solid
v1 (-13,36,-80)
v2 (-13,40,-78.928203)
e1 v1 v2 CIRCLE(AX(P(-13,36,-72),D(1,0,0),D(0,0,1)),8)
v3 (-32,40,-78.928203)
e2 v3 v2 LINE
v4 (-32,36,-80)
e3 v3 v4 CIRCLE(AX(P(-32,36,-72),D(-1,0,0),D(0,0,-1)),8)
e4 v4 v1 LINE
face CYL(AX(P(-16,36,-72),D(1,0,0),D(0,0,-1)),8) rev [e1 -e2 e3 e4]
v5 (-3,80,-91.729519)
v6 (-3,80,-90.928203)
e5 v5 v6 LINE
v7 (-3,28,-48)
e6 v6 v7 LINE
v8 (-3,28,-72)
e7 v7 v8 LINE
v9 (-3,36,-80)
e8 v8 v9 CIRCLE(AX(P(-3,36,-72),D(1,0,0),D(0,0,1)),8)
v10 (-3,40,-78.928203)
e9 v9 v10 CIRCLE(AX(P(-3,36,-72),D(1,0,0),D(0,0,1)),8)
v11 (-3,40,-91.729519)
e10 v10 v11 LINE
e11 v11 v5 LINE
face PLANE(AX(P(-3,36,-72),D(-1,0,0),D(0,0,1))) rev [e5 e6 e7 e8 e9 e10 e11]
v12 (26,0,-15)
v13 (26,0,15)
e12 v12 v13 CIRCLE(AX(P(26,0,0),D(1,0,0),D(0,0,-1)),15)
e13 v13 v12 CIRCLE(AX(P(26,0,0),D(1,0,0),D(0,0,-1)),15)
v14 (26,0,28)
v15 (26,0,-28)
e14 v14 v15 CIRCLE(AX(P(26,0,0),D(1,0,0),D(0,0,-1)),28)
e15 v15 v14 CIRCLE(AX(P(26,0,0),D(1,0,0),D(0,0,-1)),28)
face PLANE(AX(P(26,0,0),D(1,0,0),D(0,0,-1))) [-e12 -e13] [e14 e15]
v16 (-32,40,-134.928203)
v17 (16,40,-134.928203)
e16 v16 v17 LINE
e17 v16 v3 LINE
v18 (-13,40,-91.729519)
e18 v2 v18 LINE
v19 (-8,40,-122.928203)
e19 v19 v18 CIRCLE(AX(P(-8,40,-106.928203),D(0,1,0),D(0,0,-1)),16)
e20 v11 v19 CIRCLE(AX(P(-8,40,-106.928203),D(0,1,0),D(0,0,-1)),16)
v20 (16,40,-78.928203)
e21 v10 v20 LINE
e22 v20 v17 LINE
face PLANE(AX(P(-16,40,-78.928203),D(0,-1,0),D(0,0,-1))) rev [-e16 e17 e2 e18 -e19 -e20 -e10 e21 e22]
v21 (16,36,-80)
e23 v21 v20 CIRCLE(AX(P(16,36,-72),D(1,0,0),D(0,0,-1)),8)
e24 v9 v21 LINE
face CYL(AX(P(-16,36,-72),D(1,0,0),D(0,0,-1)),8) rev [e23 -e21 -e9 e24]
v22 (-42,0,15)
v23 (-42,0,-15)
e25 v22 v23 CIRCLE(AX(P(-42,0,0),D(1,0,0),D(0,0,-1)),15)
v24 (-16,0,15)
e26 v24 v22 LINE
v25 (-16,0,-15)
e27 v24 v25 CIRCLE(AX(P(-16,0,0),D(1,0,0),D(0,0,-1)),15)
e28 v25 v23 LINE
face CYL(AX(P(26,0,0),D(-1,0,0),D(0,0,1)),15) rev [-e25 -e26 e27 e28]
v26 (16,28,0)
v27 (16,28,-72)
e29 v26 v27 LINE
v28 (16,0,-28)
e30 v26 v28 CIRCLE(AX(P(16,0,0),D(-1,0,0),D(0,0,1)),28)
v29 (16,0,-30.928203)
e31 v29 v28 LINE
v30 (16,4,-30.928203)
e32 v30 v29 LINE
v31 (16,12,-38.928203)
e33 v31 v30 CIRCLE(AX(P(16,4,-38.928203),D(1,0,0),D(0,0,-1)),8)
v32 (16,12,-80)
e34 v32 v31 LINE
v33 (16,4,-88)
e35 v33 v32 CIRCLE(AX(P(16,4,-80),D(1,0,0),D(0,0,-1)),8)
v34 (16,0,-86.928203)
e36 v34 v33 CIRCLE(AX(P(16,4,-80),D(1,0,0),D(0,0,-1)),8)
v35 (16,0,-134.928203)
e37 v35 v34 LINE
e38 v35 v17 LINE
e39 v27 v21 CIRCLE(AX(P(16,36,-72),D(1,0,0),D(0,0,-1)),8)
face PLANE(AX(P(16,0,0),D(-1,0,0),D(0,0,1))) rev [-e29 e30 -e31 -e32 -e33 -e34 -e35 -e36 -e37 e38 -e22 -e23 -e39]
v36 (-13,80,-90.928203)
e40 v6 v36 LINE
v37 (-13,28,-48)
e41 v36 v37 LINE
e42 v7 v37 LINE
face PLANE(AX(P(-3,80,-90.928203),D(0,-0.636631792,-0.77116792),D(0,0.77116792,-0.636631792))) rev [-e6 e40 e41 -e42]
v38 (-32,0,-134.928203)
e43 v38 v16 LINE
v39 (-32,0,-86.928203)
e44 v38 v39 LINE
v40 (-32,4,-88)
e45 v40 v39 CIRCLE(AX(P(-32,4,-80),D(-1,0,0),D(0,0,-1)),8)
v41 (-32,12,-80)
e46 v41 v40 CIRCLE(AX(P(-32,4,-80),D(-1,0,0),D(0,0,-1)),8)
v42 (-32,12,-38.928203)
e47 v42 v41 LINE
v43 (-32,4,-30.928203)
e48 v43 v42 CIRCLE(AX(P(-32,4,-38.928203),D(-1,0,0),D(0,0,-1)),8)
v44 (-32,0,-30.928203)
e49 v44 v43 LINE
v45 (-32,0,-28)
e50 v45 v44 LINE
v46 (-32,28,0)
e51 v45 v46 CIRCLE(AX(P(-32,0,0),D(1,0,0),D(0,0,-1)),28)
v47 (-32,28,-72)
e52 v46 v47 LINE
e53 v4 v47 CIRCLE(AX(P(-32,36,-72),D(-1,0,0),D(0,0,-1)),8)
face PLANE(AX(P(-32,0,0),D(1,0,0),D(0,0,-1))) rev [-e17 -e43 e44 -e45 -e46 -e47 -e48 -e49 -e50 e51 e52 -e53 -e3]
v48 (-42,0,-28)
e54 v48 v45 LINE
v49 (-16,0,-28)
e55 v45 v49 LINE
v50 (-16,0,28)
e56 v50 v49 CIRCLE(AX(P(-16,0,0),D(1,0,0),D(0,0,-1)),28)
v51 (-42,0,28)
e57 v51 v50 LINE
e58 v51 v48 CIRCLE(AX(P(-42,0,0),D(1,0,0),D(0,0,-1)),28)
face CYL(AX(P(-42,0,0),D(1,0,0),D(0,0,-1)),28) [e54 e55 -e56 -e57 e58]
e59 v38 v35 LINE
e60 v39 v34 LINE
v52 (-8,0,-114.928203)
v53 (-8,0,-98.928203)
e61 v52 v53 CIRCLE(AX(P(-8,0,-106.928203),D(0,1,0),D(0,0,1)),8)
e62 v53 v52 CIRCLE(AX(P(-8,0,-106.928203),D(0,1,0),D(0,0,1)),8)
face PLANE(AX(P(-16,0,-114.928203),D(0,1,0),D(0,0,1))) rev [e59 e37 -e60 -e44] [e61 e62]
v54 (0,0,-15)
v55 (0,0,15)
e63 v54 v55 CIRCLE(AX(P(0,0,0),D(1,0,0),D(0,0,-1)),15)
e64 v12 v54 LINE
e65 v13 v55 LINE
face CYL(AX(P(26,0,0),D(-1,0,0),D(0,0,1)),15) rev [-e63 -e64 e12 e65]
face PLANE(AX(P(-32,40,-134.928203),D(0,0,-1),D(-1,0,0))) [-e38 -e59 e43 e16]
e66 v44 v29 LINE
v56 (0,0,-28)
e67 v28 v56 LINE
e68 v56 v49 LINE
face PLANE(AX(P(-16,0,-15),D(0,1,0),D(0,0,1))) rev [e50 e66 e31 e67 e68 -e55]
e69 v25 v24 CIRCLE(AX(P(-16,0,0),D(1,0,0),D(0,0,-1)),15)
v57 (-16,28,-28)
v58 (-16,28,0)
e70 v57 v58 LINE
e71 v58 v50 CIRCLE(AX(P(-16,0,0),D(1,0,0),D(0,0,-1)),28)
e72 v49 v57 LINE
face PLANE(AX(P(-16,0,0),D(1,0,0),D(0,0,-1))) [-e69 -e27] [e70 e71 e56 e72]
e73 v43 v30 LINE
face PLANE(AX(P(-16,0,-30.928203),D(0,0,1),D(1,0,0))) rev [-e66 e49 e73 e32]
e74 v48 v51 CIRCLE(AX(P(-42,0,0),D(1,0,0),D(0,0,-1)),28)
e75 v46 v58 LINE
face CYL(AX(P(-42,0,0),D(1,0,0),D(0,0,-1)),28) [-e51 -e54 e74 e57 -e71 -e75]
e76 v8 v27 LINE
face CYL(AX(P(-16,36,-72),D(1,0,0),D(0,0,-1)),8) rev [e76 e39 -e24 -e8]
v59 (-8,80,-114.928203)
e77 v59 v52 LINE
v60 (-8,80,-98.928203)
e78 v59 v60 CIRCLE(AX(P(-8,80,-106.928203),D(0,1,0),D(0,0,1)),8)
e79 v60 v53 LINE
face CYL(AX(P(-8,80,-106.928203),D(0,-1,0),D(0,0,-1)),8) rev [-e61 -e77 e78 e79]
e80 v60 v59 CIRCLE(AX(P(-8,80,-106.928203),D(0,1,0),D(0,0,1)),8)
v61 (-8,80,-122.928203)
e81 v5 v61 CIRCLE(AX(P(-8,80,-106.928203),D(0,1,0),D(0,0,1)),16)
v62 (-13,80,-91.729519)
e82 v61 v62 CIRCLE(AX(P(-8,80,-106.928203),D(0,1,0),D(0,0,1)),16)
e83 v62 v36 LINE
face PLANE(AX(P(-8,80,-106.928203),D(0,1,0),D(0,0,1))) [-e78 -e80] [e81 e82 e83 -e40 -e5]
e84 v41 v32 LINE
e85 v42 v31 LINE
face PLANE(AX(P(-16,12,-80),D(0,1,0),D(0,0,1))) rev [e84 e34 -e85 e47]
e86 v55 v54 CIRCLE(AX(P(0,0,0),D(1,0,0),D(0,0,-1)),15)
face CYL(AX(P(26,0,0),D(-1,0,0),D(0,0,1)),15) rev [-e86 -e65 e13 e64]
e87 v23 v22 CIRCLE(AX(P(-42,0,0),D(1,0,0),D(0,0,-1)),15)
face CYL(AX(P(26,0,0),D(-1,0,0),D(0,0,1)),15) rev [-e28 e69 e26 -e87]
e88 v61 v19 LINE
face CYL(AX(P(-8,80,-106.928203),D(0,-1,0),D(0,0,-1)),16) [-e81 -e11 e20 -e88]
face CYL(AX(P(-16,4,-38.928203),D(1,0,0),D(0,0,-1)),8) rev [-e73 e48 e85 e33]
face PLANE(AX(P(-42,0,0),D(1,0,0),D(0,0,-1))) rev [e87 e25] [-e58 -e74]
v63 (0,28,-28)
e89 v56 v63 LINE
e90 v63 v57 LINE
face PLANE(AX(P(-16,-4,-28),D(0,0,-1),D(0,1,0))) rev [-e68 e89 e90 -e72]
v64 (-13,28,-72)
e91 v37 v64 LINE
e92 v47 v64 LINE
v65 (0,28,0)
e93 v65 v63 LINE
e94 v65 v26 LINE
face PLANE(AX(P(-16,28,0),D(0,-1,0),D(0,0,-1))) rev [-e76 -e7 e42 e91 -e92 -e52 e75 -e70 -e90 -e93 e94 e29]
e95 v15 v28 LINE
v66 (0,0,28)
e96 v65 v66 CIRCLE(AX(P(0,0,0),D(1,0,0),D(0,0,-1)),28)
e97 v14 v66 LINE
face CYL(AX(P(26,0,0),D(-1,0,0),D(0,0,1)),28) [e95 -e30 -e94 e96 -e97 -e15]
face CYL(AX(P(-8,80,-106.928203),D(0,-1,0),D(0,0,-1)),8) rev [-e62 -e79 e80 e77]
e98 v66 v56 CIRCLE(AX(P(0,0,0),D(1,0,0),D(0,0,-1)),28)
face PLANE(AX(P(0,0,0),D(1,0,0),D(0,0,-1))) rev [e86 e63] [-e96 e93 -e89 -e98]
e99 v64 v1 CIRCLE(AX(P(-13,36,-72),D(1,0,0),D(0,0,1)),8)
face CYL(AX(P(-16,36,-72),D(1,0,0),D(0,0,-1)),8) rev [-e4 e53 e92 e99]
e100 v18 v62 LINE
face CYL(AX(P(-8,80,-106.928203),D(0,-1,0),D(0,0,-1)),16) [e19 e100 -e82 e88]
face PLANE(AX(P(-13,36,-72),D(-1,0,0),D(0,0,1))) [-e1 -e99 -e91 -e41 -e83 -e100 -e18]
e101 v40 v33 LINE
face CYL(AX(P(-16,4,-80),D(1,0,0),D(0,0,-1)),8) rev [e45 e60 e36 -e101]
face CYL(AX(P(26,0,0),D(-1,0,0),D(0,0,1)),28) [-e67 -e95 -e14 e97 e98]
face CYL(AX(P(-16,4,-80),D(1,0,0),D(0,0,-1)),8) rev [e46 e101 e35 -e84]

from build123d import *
from build123d.topology import SkipClean

# Parameters (mm, degrees)
CLEVIS_LUG_1_SKETCH_R     = 28
CLEVIS_LUG_1_SKETCH_R_2   = 15
CLEVIS_LUG_1_56X_30_DEPTH = 26
CLEVIS_LUG_2_SKETCH_R     = 28
CLEVIS_LUG_2_SKETCH_R_2   = 15
CLEVIS_LUG_2_56X_30_DEPTH = 26
ARM_START                 = -16
ARM_BODY_DEPTH            = 16
ARM_EXTENSION_DEPTH       = 16
FORK_SLOT_SKETCH_W        = 16
FORK_SLOT_SKETCH_H        = 28
FORK_SLOT_CUT_DEPTH       = 32
PIVOT_BLOCK_SKETCH_W      = 39.579982786
PIVOT_BLOCK_SKETCH_H      = 40
PIVOT_BLOCK_DEPTH         = 48
TOP_PIVOT_BOSS_SKETCH_R   = 16
TOP_PIVOT_BOSS_SKETCH_R_2 = 8
TOP_PIVOT_BOSS_32_DEPTH   = 40
PIVOT_START               = -40
PIVOT_BORE_SKETCH_R       = 8
PIVOT_BORE_16_DEPTH       = 40
BOSS_GUSSET_DEPTH         = 5


with BuildPart() as part:
    # Clevis Lug 1 Sketch → Clevis Lug 1 Ø56xØ30 (new body)
    with BuildSketch(Plane(origin=(0, 0, 0), x_dir=(0, 0, -1), z_dir=(1, 0, 0))):
        with Locations(Location((0, 0, 0), (0, 0, 180))):
            Circle(CLEVIS_LUG_1_SKETCH_R)
        with Locations(Location((0, 0, 0), (0, 0, 180))):
            Circle(CLEVIS_LUG_1_SKETCH_R_2, mode=Mode.SUBTRACT)
    extrude(amount=CLEVIS_LUG_1_56X_30_DEPTH)



with BuildPart() as body_2:
    # Clevis Lug 2 Sketch → Clevis Lug 2 Ø56xØ30 (new body)
    with BuildSketch(Plane(origin=(-16, 0, 0), x_dir=(0, 0, -1), z_dir=(1, 0, 0))):
        with Locations(Location((0, 0, 0), (0, 0, 180))):
            Circle(CLEVIS_LUG_2_SKETCH_R)
        with Locations(Location((0, 0, 0), (0, 0, 180))):
            Circle(CLEVIS_LUG_2_SKETCH_R_2, mode=Mode.SUBTRACT)
    extrude(amount=-CLEVIS_LUG_2_56X_30_DEPTH)

    # Arm Profile Sketch → Arm Body (add)
    with BuildSketch(Plane(origin=(-16, 0, 0), x_dir=(0, 0, -1), z_dir=(1, 0, 0)).offset(ARM_START)):
        with BuildLine():
            Line((72, 28), (0, 28))
            ThreePointArc((0, 28), (19.798989873, 19.798989873), (28, 0))
            Line((28, 0), (30.92820323, 0))
            Line((30.92820323, 0), (30.92820323, 4))
            ThreePointArc((30.92820323, 4), (33.271348981, 9.656854249), (38.92820323, 12))
            Line((38.92820323, 12), (72, 12))
            Line((72, 12), (80, 12))
            ThreePointArc((80, 12), (86.92820323, 8), (86.92820323, 0))
            Line((86.92820323, 0), (114.92820323, 0))
            Line((114.92820323, 0), (114.92820323, 40))
            Line((114.92820323, 40), (78.92820323, 40))
            ThreePointArc((78.92820323, 40), (78.92820323, 32), (72, 28))
        make_face()
    extrude(amount=ARM_BODY_DEPTH)


with BuildPart() as part_1:
    with SkipClean():  # the faces are left unmerged after this step: merging them gives an invalid solid
        add(part.part)

        add(body_2.part)  # Arm Extension merges body 2
        # Arm Extension Sketch → Arm Extension (add, symmetric)
        with BuildSketch(Plane.ZY):
            with BuildLine():
                Line((0, 28), (-72, 28))
                ThreePointArc((-72, 28), (-78.92820323, 32), (-78.92820323, 40))
                Line((-78.92820323, 40), (-114.92820323, 40))
                Line((-114.92820323, 40), (-114.92820323, 0))
                Line((-114.92820323, 0), (-86.92820323, 0))
                ThreePointArc((-86.92820323, 0), (-86.92820323, 8), (-80, 12))
                Line((-80, 12), (-38.92820323, 12))
                ThreePointArc((-38.92820323, 12), (-33.271348981, 9.656854249), (-30.92820323, 4))
                Line((-30.92820323, 4), (-30.92820323, 0))
                Line((-30.92820323, 0), (-15, 0))
                ThreePointArc((-15, 0), (-10.606601718, 10.606601718), (0, 15))
                Line((0, 15), (0, 28))
            make_face()
        extrude(amount=ARM_EXTENSION_DEPTH, both=True)

    # Fork Slot Sketch → Fork Slot Cut (cut)
    with BuildSketch(Plane(origin=(0, 28, 0), x_dir=(1, 0, 0), z_dir=(0, 1, 0))):
        with Locations((-8, 14)):
            Rectangle(FORK_SLOT_SKETCH_W, FORK_SLOT_SKETCH_H)
    extrude(amount=-FORK_SLOT_CUT_DEPTH, mode=Mode.SUBTRACT)

    # Pivot Block Sketch → Pivot Block (add)
    with BuildSketch(Plane(origin=(16, 0, 0), x_dir=(0, 0, -1), z_dir=(1, 0, 0))):
        with Locations((115.138211837, 20)):
            Rectangle(PIVOT_BLOCK_SKETCH_W, PIVOT_BLOCK_SKETCH_H)
    extrude(amount=-PIVOT_BLOCK_DEPTH)

    # Top Pivot Boss Sketch → Top Pivot Boss Ø32 (add)
    with BuildSketch(Plane(origin=(0, 40, 0), x_dir=(1, 0, 0), z_dir=(0, 1, 0))):
        with Locations(Location((-8, 106.92820323, 0), (0, 0, 90))):
            Circle(TOP_PIVOT_BOSS_SKETCH_R)
        with Locations(Location((-8, 106.92820323, 0), (0, 0, 270))):
            Circle(TOP_PIVOT_BOSS_SKETCH_R_2, mode=Mode.SUBTRACT)
    extrude(amount=TOP_PIVOT_BOSS_32_DEPTH)

    # Pivot Bore Sketch → Pivot Bore Ø16 (cut)
    with BuildSketch(Plane(origin=(0, 40, 0), x_dir=(1, 0, 0), z_dir=(0, 1, 0)).offset(PIVOT_START)):
        with Locations(Location((-8, 106.92820323, 0), (0, 0, 270))):
            Circle(PIVOT_BORE_SKETCH_R)
    extrude(amount=PIVOT_BORE_16_DEPTH, mode=Mode.SUBTRACT)

    # Boss Gusset Sketch → Boss Gusset (add, symmetric)
    with BuildSketch(Plane(origin=(-8, 0, 0), x_dir=(0, 0, -1), z_dir=(1, 0, 0))):
        with BuildLine():
            Line((90.92820323, 80), (48, 28))
            Line((48, 28), (72, 28))
            ThreePointArc((72, 28), (78.92820323, 32), (78.92820323, 40))
            Line((78.92820323, 40), (93.443690624, 40))
            Line((93.443690624, 40), (93.443690624, 80))
            Line((93.443690624, 80), (90.92820323, 80))
        make_face()
    extrude(amount=BOSS_GUSSET_DEPTH, both=True)


solid = part_1.part
